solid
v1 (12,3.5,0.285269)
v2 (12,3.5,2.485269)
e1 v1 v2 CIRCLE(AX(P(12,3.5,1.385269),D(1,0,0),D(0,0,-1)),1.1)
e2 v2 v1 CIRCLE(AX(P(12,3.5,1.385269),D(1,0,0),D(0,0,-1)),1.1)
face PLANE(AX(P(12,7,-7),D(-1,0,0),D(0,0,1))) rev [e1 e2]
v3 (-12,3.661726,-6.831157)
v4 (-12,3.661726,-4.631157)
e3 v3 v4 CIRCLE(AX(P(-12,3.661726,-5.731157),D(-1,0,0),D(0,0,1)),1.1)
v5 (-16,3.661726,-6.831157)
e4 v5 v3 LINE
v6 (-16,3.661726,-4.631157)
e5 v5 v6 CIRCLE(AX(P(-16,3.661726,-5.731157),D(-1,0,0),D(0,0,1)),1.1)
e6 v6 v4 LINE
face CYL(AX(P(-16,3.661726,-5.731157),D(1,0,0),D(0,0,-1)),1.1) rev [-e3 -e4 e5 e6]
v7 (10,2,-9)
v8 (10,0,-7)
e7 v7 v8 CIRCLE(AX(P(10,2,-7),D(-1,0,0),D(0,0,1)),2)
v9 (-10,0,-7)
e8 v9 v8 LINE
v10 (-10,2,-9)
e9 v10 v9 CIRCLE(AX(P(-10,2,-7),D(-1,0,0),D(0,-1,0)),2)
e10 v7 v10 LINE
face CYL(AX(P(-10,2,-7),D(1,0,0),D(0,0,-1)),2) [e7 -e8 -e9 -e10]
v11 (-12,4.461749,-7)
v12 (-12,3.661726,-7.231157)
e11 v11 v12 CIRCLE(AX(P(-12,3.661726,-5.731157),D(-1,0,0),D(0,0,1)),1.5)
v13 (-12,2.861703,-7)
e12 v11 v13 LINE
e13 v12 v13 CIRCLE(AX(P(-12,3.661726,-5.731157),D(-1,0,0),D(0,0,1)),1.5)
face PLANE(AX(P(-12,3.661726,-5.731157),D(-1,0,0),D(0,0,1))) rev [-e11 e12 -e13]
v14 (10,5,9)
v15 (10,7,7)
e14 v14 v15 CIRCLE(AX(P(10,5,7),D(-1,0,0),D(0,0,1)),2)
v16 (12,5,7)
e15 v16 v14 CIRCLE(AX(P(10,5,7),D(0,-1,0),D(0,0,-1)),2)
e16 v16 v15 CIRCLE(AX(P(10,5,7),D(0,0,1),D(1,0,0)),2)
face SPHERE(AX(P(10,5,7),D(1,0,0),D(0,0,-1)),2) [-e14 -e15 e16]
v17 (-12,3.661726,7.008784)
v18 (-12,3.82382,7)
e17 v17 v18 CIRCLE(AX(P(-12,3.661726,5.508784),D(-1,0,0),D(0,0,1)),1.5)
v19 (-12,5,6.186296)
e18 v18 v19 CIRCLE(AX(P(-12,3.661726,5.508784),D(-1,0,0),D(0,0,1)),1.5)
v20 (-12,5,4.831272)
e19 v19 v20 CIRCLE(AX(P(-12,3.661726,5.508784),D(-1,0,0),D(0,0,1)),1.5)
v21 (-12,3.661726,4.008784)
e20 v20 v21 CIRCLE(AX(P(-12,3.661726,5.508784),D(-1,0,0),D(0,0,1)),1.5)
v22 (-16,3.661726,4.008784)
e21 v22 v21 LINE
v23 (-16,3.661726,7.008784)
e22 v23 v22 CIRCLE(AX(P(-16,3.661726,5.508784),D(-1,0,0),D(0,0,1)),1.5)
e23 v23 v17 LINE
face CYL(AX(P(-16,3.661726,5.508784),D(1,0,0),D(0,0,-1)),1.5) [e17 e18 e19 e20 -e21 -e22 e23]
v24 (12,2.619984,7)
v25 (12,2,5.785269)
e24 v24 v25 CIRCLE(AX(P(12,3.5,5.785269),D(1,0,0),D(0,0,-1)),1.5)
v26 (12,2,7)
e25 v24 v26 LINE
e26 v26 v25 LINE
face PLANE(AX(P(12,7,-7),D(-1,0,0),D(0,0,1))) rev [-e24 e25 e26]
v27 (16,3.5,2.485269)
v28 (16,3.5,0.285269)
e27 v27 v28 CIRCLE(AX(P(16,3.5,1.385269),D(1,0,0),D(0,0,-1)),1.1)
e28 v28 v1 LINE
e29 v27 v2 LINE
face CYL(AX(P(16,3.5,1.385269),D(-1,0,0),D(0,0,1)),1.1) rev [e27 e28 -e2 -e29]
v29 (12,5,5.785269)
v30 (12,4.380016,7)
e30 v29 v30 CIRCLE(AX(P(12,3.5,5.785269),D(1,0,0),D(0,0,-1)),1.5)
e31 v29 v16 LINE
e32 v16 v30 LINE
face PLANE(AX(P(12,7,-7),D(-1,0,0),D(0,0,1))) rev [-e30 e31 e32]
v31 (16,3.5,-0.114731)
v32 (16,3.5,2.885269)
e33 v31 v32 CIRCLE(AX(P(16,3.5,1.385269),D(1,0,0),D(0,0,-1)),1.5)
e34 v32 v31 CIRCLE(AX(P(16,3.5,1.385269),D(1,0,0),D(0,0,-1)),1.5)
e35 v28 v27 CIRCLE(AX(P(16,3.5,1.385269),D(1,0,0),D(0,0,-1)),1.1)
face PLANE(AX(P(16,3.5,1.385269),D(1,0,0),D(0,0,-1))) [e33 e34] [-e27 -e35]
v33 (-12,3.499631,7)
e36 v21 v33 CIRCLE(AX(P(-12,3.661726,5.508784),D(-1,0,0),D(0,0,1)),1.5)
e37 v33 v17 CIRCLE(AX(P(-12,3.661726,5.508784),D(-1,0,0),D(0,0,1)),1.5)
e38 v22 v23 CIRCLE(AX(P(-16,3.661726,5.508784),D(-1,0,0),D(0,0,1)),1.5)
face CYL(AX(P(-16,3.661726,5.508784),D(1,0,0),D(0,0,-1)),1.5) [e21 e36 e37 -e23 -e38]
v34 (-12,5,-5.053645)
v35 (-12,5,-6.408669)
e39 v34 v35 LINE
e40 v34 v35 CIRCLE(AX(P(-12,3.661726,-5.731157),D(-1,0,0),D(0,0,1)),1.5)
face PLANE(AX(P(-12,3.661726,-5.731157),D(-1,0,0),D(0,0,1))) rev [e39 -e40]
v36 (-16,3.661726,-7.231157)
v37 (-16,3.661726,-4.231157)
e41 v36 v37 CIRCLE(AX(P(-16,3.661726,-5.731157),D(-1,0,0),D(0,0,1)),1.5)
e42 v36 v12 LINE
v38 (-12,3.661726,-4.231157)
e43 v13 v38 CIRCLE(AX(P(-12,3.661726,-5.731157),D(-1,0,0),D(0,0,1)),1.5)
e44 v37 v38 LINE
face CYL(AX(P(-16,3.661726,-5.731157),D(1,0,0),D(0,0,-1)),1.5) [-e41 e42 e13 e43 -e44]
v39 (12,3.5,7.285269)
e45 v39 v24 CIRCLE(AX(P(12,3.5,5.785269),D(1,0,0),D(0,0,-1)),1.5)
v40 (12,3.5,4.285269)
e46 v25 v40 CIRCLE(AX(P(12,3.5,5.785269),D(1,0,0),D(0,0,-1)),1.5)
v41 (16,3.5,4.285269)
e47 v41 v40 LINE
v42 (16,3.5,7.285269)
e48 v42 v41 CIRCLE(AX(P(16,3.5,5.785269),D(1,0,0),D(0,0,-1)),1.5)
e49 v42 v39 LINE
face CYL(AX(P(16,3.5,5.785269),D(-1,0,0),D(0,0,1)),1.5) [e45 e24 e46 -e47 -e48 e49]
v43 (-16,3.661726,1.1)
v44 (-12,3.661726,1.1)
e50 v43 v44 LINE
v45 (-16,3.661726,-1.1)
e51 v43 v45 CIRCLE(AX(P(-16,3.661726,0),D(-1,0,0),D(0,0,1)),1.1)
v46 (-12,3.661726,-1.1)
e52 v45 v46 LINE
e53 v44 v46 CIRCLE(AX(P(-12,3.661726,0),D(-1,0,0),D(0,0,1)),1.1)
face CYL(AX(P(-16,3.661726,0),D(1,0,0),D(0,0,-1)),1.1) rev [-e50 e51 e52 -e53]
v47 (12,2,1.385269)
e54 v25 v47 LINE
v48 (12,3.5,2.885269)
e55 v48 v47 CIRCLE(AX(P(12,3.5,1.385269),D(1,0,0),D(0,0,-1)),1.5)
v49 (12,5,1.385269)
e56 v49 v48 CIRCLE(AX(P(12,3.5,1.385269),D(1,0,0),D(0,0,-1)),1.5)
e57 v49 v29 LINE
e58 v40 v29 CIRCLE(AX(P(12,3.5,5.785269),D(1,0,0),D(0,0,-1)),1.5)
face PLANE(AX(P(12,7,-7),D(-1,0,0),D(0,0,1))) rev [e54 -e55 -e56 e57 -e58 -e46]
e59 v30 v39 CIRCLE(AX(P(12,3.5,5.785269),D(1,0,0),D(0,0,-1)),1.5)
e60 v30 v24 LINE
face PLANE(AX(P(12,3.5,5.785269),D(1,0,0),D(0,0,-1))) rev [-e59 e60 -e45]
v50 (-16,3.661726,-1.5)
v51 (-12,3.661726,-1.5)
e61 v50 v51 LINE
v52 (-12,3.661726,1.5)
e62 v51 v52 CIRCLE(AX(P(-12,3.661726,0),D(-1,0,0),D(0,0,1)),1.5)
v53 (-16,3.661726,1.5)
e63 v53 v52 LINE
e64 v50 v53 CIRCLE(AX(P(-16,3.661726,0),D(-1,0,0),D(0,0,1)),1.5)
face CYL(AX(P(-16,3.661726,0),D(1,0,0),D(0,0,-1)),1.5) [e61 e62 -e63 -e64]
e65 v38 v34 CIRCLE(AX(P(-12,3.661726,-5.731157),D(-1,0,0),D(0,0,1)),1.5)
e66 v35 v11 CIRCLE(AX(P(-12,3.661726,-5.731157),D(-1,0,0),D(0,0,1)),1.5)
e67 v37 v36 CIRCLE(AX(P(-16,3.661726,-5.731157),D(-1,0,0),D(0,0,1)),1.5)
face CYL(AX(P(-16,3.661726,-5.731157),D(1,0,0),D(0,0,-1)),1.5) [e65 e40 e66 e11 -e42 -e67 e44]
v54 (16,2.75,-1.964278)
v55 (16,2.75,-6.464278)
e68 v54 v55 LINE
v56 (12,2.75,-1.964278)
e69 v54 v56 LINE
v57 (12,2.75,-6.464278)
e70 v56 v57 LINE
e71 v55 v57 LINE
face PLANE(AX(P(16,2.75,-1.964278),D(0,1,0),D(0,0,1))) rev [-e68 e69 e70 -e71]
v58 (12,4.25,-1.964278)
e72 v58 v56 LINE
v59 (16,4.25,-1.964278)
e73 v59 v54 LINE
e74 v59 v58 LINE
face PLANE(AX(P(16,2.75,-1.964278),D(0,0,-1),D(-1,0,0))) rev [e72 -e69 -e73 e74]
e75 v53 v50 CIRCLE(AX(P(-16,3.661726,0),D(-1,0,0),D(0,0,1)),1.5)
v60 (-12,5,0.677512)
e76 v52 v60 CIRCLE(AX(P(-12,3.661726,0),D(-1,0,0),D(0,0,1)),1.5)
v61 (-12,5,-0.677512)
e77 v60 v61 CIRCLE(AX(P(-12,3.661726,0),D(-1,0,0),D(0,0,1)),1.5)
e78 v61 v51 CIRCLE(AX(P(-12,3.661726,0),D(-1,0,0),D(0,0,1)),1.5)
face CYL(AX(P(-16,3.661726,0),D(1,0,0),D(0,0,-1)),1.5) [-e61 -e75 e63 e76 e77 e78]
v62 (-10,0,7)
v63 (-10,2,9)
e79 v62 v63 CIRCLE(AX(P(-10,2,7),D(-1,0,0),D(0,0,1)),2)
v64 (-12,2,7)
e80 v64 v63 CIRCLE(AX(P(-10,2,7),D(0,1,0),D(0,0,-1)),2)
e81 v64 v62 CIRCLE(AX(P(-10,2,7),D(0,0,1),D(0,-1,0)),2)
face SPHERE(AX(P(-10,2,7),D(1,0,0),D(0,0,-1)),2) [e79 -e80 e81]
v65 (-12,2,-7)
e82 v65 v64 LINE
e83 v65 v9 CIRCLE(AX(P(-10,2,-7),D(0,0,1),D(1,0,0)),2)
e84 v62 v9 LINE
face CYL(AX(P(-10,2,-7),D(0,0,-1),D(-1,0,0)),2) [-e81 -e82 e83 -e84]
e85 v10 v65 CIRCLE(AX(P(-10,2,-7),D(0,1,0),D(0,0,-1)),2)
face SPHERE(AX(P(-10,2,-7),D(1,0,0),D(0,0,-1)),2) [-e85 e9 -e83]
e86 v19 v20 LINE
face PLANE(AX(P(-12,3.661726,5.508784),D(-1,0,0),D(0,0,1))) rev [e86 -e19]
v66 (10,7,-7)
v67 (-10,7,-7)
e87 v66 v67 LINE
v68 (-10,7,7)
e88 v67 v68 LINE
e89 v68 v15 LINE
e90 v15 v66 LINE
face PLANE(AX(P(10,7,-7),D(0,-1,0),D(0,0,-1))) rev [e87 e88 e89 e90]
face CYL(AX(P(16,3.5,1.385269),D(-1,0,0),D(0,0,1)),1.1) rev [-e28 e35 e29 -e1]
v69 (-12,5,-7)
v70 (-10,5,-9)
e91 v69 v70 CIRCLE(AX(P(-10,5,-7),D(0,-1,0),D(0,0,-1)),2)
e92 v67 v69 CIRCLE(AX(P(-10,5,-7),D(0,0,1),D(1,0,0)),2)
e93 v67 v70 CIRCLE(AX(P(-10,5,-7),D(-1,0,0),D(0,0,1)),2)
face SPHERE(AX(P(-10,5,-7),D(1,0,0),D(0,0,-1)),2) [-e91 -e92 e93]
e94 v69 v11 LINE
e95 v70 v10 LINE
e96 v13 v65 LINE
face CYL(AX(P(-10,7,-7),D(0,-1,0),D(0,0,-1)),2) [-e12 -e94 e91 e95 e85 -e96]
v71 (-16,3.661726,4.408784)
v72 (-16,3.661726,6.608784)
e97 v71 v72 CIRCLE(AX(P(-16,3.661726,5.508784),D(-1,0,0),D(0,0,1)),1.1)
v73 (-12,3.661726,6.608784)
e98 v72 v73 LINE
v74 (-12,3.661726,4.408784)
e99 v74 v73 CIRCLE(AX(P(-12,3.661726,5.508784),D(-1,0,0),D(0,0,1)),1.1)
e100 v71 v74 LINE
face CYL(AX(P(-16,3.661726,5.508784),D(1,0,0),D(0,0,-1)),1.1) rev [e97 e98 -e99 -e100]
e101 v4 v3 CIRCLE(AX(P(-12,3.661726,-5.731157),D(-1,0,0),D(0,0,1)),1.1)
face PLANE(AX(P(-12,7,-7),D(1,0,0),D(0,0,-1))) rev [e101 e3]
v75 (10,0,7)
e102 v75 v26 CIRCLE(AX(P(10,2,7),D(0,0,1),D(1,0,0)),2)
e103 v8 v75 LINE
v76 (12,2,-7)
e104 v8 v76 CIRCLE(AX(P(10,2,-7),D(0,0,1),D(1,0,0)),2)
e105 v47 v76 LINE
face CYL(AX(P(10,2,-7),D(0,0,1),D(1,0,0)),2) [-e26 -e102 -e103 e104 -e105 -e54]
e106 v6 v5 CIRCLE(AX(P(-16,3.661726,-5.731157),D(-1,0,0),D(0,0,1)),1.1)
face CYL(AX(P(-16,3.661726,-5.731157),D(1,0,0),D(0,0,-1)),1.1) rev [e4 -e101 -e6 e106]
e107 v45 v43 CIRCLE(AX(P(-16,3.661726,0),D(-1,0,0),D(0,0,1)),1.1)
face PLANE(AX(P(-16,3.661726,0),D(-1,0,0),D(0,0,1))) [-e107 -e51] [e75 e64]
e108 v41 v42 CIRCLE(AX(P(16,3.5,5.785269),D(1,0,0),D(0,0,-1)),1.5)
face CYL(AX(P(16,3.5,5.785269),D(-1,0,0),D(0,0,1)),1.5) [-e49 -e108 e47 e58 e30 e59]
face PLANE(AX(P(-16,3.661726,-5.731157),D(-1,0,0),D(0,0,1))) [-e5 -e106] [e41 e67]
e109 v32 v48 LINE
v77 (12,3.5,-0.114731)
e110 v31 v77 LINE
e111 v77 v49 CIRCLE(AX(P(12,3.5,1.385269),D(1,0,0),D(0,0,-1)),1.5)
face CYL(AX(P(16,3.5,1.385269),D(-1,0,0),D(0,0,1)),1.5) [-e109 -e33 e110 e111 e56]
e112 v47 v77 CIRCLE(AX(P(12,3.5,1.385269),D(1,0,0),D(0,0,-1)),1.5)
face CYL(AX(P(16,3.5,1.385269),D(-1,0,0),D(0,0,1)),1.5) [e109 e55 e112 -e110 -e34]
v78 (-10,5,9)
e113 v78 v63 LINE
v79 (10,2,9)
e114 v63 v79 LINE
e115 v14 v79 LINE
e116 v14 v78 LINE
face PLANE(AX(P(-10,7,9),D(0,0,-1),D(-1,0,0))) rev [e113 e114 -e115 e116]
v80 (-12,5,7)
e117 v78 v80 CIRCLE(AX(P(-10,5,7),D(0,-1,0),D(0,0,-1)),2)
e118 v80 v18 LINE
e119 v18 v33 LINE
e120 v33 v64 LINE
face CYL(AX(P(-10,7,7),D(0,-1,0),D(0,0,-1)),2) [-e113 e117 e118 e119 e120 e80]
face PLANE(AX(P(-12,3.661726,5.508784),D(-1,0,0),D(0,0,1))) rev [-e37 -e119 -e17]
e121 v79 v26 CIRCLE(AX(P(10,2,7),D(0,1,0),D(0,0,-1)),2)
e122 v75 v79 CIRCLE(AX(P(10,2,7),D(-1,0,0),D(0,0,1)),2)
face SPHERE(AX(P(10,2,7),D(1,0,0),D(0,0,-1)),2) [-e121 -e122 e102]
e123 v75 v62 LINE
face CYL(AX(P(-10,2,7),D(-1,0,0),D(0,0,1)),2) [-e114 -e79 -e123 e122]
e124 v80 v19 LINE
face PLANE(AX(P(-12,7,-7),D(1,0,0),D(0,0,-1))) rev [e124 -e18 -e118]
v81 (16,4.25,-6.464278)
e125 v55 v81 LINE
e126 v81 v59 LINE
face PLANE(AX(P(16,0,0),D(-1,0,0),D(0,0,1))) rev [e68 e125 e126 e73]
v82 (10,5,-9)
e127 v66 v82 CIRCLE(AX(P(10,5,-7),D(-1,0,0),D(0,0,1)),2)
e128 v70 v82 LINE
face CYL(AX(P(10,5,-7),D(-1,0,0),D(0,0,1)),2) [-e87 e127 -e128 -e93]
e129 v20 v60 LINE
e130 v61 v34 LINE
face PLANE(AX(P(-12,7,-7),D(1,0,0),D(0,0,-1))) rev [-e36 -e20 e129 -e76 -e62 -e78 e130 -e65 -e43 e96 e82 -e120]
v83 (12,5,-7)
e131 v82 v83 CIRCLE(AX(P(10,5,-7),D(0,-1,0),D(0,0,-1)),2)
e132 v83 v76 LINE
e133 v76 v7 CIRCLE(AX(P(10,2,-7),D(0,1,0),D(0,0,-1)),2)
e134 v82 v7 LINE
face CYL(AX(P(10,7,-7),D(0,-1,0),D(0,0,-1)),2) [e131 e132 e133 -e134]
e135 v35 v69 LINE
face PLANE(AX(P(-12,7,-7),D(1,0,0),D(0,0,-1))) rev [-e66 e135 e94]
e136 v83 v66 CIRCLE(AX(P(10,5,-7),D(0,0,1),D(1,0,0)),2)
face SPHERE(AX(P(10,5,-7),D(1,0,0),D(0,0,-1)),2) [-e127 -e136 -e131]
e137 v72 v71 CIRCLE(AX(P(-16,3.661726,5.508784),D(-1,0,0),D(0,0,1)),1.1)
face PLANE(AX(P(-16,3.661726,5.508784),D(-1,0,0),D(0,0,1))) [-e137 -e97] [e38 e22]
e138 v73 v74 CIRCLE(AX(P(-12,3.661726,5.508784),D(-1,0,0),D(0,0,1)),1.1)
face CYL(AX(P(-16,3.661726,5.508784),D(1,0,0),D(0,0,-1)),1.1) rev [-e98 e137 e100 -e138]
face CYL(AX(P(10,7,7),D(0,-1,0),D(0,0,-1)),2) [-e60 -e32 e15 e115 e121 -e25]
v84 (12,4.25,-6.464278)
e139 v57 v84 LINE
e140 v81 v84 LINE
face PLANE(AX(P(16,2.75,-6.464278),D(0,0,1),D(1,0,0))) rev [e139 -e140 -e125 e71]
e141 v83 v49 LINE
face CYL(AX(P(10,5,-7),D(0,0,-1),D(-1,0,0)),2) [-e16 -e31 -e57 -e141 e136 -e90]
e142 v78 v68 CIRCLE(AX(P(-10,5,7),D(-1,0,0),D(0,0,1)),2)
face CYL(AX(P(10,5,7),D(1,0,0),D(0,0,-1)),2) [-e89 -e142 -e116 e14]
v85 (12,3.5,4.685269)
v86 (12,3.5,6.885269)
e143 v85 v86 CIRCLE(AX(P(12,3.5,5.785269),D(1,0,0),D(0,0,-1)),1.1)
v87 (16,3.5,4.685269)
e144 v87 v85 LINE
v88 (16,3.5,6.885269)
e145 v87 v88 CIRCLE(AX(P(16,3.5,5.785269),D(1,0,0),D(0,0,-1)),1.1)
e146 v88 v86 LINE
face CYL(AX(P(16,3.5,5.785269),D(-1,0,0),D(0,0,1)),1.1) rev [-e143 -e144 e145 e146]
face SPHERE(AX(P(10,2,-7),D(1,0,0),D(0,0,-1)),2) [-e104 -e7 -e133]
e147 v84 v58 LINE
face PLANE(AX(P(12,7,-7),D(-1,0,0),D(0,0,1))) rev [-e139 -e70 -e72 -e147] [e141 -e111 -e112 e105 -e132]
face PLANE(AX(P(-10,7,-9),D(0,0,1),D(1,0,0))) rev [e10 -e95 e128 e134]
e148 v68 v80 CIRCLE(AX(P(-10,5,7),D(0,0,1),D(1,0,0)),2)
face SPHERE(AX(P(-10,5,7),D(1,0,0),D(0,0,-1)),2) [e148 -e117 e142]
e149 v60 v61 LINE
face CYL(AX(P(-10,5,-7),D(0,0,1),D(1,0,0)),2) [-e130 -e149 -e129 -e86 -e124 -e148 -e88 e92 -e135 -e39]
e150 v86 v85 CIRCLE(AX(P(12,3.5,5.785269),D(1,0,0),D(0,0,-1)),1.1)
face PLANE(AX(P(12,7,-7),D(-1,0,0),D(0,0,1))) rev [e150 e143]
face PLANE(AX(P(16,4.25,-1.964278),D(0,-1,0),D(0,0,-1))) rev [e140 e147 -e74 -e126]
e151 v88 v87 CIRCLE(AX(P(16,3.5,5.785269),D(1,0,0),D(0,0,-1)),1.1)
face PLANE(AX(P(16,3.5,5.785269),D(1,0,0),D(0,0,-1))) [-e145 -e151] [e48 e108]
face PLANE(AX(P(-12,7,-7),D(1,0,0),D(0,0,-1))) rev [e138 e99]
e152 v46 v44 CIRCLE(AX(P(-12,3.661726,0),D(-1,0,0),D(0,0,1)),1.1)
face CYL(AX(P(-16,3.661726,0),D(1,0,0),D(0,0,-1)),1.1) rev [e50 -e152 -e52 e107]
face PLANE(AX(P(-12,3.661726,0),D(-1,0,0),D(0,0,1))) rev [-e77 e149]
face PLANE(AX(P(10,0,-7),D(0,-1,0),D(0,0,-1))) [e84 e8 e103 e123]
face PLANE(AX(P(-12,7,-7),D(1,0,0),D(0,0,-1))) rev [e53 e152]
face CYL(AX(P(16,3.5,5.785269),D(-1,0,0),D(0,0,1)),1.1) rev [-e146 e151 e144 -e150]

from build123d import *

# Parameters (mm, degrees)
HOUSING_BODY_DEPTH               = 7
HOUSING_EDGE_FILLET_R2_R         = 2
PIN_SET_A_SKETCH_R               = 1.5
PIN_SET_A_SKETCH_R_2             = 1.1
TUBULAR_PINS_SET_A_3_DEPTH       = 4
PIN_SET_B_AND_TAB_SKETCH_R       = 1.5
PIN_SET_B_AND_TAB_SKETCH_R_2     = 1.1
PIN_SET_B_AND_TAB_SKETCH_W       = 4.5
PIN_SET_B_AND_TAB_SKETCH_H       = 1.5
TUBULAR_PINS_SET_B_AND_TAB_DEPTH = 4


with BuildPart() as part:
    # Housing Profile Sketch → Housing Body (new body)
    with BuildSketch(Plane(origin=(0, 0, 0), x_dir=(1, 0, 0), z_dir=(0, 1, 0))):
        with BuildLine():
            Line((-10, 9), (10, 9))
            ThreePointArc((10, 9), (11.414213562, 8.414213562), (12, 7))
            Line((12, 7), (12, -7))
            ThreePointArc((12, -7), (11.414213562, -8.414213562), (10, -9))
            Line((10, -9), (-10, -9))
            ThreePointArc((-10, -9), (-11.414213562, -8.414213562), (-12, -7))
            Line((-12, -7), (-12, 7))
            ThreePointArc((-12, 7), (-11.414213562, 8.414213562), (-10, 9))
        make_face()
    extrude(amount=HOUSING_BODY_DEPTH)

    # Housing Edge Fillet R2
    housing_edge_fillet_r2_edges = [part.edges().sort_by_distance(p)[0] for p in [
        (-12, 0, 0),
        (-11.414213562, 0, -8.414213562),
        (0, 0, -9),
        (11.414213562, 0, -8.414213562),
        (-11.414213562, 7, -8.414213562),
        (-12, 7, 0),
        (-11.414213562, 7, 8.414213562),
        (0, 7, 9),
        (11.414213562, 7, 8.414213562),
        (12, 7, 0),
        (11.414213562, 7, -8.414213562),
        (12, 0, 0),
        (0, 7, -9),
        (11.414213562, 0, 8.414213562),
        (0, 0, 9),
        (-11.414213562, 0, 8.414213562),
    ]]
    fillet(housing_edge_fillet_r2_edges, radius=HOUSING_EDGE_FILLET_R2_R)

    # Pin Set A Sketch → Tubular Pins Set A Ø3 (add)
    # profile 1 of 3: a face of its own
    with BuildSketch(Plane.ZY.offset(12)):
        with Locations(Location((0, 3.661725767, 0), (0, 0, 116.851166023))):
            Circle(PIN_SET_A_SKETCH_R)
        with Locations((0, 3.661725767)):
            Circle(PIN_SET_A_SKETCH_R_2, mode=Mode.SUBTRACT)
    # profile 2 of 3: a face of its own
    with BuildSketch(Plane.ZY.offset(12)):
        with Locations(Location((-5.731156871, 3.661725767, 0), (0, 0, 212.232000091))):
            Circle(PIN_SET_A_SKETCH_R)
        with Locations((-5.731156871, 3.661725767)):
            Circle(PIN_SET_A_SKETCH_R_2, mode=Mode.SUBTRACT)
    # profile 3 of 3: a face of its own
    with BuildSketch(Plane.ZY.offset(12)):
        with Locations(Location((5.508783942, 3.661725767, 0), (0, 0, 116.851166023))):
            Circle(PIN_SET_A_SKETCH_R)
        with Locations((5.508783942, 3.661725767)):
            Circle(PIN_SET_A_SKETCH_R_2, mode=Mode.SUBTRACT)
    extrude(amount=TUBULAR_PINS_SET_A_3_DEPTH)

    # Pin Set B and Tab Sketch → Tubular Pins Set B and Tab (add)
    # profile 1 of 3: a face of its own
    with BuildSketch(Plane(origin=(12, 0, 0), x_dir=(0, 0, -1), z_dir=(1, 0, 0))):
        with Locations(Location((-5.785268851, 3.5, 0), (0, 0, 215.921576532))):
            Circle(PIN_SET_B_AND_TAB_SKETCH_R)
        with Locations((-5.785268851, 3.5)):
            Circle(PIN_SET_B_AND_TAB_SKETCH_R_2, mode=Mode.SUBTRACT)
    # profile 2 of 3: a face of its own
    with BuildSketch(Plane(origin=(12, 0, 0), x_dir=(0, 0, -1), z_dir=(1, 0, 0))):
        with Locations(Location((-1.385268851, 3.5, 0), (0, 0, 270))):
            Circle(PIN_SET_B_AND_TAB_SKETCH_R)
        with Locations((-1.385268851, 3.5)):
            Circle(PIN_SET_B_AND_TAB_SKETCH_R_2, mode=Mode.SUBTRACT)
    # profile 3 of 3: a face of its own
    with BuildSketch(Plane(origin=(12, 0, 0), x_dir=(0, 0, -1), z_dir=(1, 0, 0))):
        with Locations((4.21427792, 3.5)):
            Rectangle(PIN_SET_B_AND_TAB_SKETCH_W, PIN_SET_B_AND_TAB_SKETCH_H)
    extrude(amount=TUBULAR_PINS_SET_B_AND_TAB_DEPTH)


solid = part.part
